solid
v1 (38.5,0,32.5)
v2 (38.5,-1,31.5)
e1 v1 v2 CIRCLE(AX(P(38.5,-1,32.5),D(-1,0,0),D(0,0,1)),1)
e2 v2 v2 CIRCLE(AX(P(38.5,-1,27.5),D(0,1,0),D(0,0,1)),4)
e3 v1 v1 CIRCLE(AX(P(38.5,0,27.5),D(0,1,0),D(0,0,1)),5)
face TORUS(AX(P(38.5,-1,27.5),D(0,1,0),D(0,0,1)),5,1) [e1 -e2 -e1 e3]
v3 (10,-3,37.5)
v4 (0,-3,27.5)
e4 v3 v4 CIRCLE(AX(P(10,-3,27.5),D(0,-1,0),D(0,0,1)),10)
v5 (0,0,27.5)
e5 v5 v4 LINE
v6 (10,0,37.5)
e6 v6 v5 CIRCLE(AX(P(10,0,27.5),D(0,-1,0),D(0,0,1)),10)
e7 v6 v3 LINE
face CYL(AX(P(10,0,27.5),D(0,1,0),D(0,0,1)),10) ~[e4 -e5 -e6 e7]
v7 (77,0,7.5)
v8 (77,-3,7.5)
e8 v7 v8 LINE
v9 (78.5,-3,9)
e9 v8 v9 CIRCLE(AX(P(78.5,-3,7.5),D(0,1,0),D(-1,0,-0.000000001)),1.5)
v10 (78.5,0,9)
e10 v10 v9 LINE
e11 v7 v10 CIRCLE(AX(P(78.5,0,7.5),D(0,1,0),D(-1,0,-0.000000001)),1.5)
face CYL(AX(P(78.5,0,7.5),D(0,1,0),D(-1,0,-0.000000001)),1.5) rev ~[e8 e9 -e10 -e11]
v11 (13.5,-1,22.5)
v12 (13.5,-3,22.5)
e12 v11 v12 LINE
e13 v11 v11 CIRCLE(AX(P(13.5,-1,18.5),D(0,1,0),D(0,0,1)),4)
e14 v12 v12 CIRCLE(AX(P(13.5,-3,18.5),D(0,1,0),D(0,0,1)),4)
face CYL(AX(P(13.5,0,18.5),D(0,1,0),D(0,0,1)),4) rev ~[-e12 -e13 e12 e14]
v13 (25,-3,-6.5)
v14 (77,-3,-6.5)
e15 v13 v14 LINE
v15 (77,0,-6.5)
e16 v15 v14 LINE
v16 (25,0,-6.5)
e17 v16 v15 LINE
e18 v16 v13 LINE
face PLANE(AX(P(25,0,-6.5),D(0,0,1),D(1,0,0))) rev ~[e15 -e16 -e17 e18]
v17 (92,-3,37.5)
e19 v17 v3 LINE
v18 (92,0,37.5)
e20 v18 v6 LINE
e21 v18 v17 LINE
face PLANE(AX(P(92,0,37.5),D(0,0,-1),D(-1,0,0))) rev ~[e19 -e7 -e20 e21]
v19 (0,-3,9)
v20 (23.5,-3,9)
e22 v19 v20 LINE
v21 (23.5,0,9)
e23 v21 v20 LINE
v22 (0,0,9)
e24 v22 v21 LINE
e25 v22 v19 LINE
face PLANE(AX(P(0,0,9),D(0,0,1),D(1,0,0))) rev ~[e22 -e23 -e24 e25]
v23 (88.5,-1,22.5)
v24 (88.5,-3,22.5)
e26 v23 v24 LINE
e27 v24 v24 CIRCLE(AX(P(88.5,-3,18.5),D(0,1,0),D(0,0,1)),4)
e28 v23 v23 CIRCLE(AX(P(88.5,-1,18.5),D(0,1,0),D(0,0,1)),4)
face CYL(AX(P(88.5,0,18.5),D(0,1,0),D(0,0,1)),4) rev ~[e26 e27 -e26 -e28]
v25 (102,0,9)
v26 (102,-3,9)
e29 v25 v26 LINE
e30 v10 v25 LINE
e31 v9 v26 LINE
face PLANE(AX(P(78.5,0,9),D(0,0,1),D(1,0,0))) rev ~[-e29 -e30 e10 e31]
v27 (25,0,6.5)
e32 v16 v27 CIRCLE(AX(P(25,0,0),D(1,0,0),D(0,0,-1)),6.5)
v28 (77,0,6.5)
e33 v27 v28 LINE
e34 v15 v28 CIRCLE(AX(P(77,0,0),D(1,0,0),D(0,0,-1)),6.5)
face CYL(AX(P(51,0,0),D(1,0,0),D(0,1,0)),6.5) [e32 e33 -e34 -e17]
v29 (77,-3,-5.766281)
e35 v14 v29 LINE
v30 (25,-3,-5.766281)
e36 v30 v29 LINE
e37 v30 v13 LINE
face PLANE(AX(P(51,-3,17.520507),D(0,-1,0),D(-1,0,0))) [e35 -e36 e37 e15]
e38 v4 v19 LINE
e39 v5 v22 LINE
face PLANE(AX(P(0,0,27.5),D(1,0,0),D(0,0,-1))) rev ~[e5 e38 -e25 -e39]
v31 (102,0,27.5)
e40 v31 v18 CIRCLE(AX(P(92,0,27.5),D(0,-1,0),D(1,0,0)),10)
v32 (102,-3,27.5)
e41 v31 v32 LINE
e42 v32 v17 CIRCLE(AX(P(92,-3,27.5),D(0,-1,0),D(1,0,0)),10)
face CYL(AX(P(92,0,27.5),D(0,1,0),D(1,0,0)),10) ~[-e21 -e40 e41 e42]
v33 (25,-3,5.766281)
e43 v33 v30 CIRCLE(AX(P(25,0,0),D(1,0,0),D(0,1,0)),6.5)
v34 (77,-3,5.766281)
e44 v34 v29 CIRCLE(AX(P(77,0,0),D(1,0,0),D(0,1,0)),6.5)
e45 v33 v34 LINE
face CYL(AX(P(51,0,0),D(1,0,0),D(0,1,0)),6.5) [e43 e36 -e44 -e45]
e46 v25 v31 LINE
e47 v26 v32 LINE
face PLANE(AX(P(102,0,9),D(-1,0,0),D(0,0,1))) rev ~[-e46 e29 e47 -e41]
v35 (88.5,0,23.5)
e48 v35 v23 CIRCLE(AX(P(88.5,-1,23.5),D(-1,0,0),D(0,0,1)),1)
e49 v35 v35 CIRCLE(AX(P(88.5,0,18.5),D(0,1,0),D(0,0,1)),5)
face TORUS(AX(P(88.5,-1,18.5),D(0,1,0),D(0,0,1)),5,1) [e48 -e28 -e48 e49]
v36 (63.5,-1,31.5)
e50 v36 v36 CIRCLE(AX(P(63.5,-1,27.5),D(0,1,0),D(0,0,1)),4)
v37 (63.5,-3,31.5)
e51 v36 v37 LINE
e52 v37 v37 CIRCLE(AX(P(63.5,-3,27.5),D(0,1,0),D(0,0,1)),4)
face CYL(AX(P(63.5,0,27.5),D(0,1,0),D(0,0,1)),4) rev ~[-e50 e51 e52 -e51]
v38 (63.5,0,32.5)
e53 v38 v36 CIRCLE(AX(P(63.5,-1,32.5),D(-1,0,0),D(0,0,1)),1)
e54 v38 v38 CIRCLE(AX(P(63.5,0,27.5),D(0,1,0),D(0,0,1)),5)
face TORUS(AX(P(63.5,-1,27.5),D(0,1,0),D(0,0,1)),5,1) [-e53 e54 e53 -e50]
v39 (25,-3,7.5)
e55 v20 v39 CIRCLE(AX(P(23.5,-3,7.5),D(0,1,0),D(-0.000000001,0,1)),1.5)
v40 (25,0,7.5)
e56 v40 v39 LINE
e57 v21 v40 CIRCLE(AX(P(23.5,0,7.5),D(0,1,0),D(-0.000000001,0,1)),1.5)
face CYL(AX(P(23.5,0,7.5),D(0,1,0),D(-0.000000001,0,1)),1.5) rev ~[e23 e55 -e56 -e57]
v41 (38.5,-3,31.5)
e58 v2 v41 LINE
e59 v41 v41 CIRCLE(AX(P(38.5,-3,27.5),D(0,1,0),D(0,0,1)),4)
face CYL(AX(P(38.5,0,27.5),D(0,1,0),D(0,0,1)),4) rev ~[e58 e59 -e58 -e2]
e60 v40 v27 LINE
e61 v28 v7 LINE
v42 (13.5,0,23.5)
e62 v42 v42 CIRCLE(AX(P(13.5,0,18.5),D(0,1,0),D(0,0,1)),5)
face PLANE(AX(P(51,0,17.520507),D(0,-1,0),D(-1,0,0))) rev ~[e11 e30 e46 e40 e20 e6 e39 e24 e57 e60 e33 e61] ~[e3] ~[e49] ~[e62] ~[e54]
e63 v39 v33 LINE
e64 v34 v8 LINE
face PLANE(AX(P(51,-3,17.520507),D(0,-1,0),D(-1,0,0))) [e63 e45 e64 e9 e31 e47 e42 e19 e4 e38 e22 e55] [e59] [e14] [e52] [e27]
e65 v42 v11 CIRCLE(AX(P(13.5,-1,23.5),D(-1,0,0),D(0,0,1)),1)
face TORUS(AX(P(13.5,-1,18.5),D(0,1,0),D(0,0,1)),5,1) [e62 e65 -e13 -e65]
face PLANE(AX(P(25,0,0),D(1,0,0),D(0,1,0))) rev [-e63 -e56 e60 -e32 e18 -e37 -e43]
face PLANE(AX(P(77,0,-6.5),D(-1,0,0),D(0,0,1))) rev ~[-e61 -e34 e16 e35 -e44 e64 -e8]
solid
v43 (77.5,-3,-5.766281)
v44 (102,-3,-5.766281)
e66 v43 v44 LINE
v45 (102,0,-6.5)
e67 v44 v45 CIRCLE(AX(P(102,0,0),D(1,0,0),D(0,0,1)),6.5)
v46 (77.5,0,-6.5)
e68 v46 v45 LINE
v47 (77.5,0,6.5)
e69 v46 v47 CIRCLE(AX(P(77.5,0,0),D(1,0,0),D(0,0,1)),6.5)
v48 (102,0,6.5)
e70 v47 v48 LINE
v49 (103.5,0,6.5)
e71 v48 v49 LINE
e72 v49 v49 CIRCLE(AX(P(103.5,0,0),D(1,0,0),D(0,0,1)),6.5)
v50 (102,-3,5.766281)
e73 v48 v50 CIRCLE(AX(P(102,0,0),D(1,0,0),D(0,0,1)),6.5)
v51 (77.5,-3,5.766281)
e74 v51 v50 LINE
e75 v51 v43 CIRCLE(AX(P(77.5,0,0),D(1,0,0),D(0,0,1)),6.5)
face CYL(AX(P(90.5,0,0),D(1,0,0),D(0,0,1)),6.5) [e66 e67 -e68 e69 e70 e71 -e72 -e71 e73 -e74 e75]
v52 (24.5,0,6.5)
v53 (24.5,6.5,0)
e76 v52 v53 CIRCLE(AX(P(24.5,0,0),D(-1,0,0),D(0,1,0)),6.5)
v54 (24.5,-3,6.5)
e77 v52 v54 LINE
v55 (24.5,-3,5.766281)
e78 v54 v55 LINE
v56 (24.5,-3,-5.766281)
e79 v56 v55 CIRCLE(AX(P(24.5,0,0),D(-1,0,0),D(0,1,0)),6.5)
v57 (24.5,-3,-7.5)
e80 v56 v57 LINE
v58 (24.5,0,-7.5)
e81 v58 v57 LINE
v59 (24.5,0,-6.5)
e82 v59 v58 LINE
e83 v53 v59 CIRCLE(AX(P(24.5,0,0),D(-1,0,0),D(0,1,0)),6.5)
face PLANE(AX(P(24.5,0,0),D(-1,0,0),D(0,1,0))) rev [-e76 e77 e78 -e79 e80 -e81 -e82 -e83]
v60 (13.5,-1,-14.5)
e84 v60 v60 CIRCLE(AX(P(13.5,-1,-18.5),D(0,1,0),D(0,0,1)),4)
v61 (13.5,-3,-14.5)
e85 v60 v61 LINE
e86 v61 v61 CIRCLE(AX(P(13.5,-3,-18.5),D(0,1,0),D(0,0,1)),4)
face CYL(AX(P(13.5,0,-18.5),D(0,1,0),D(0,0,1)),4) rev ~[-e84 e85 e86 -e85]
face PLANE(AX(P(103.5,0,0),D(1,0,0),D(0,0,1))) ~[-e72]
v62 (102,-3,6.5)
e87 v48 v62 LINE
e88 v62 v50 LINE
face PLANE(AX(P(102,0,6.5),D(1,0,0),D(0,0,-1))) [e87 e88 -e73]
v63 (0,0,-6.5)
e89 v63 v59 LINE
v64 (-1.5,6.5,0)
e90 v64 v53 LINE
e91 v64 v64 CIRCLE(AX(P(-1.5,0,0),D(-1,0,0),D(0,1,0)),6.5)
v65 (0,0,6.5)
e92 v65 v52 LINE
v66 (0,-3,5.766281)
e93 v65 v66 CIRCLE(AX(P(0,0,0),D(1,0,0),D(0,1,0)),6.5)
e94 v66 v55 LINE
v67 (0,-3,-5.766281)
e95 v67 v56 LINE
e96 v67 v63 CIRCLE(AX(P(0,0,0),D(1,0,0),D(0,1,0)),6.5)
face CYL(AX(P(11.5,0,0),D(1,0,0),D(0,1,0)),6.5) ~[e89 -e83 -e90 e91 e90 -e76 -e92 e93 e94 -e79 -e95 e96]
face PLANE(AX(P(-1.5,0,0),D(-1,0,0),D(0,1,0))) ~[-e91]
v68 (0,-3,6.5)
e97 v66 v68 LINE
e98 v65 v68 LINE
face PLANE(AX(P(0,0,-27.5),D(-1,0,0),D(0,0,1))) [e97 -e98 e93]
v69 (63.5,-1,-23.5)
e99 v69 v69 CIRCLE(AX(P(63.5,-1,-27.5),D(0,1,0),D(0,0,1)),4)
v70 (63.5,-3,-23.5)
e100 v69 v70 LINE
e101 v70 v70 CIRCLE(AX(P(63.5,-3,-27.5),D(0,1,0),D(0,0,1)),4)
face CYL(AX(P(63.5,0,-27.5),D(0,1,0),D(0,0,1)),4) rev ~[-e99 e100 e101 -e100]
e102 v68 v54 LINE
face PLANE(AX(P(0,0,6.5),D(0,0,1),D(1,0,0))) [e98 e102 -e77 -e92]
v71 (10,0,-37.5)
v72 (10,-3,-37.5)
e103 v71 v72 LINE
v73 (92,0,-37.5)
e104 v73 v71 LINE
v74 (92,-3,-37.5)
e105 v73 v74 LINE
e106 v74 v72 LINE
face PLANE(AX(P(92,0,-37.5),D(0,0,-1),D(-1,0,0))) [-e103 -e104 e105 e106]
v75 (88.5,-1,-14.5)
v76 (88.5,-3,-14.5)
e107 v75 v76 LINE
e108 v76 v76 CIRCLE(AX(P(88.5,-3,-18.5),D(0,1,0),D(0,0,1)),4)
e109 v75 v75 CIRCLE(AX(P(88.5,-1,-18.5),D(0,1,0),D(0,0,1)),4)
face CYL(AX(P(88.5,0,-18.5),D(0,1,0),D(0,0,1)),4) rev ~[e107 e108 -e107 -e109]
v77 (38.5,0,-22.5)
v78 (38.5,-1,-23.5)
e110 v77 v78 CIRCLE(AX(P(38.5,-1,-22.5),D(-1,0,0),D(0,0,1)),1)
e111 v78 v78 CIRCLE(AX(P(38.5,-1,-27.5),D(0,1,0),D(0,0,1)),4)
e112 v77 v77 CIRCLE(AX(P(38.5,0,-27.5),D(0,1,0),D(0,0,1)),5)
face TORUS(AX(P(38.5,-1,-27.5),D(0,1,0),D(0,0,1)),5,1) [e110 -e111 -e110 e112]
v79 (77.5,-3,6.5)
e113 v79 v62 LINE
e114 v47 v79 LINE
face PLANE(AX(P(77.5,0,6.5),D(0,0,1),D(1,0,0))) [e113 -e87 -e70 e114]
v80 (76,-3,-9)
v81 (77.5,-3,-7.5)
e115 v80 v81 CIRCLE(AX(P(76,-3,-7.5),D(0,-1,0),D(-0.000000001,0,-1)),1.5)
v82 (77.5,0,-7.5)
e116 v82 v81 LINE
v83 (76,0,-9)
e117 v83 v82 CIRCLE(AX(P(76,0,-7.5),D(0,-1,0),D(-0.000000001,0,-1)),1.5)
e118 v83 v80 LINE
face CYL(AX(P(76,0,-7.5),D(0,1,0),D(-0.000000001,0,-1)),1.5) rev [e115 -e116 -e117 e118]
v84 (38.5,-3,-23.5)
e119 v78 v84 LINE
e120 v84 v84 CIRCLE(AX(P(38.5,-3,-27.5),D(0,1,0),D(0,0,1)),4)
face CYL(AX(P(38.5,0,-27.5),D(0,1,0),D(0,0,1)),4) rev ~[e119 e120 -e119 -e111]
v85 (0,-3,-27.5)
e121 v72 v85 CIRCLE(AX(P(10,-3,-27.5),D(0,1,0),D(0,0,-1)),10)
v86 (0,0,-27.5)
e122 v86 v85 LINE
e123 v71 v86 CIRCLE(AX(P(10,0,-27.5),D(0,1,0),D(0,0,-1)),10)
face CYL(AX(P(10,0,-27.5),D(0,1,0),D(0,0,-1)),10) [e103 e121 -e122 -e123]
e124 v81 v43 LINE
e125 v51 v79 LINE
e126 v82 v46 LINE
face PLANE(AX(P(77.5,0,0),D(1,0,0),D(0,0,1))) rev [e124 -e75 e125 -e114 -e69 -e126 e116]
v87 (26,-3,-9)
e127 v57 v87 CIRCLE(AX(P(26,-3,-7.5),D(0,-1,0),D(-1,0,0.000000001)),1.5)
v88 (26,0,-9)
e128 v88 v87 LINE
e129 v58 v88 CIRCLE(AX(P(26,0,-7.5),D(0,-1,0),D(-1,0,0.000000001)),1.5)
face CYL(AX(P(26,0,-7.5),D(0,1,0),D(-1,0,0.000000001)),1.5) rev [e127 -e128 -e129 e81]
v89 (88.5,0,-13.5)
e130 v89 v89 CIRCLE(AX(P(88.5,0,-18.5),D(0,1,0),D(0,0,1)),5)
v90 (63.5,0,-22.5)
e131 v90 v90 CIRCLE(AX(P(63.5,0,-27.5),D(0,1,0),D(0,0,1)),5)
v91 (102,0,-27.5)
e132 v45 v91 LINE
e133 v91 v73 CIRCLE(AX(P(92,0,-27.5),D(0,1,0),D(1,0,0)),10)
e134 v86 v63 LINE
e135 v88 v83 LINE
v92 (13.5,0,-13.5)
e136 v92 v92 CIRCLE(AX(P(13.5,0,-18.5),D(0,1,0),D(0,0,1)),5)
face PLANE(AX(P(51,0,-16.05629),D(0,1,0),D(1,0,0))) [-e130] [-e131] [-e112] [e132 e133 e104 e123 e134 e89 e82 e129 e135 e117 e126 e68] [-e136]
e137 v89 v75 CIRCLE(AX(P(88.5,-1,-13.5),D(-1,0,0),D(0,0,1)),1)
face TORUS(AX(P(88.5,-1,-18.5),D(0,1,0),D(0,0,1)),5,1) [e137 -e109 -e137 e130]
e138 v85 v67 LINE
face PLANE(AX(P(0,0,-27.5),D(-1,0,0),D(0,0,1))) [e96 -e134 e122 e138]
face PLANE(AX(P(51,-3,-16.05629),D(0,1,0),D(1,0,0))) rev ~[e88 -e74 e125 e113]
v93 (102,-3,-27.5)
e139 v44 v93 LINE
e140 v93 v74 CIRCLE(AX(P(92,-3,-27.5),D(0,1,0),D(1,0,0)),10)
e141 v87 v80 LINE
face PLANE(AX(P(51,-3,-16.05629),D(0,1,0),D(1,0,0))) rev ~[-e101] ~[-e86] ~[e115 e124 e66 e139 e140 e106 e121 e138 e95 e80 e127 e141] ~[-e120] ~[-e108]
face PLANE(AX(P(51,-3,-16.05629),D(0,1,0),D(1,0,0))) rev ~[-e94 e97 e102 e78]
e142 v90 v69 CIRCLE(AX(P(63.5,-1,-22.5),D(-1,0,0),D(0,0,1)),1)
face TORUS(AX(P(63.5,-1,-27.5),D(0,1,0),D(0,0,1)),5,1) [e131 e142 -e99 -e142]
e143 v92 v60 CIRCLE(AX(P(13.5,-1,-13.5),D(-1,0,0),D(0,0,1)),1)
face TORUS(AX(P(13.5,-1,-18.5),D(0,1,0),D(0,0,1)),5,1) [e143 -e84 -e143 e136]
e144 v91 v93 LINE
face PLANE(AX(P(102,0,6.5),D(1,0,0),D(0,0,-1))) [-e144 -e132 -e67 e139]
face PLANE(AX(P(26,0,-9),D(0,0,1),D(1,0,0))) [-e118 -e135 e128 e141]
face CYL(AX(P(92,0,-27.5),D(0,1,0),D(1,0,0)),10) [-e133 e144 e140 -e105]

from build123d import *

# Parameters (mm, degrees)
HINGE_LEAVES_3MM_DEPTH        = 3
HINGE_LEAVES_3MM_2_DEPTH      = 3
SCREW_HOLES_PROFILE_R         = 4
SCREW_HOLES_8X_8_DEPTH        = 3
SCREW_HOLE_EDGE_FILLET_R1_A_R = 1
SCREW_HOLE_EDGE_FILLET_R1_B_R = 1
END_KNUCKLE_1_PROFILE_W       = 26
END_KNUCKLE_1_PROFILE_H       = 6.5
CENTRE_KNUCKLE_PROFILE_W      = 52
CENTRE_KNUCKLE_PROFILE_H      = 6.5
END_KNUCKLE_2_PROFILE_W       = 26
END_KNUCKLE_2_PROFILE_H       = 6.5


with BuildPart() as part:
    # Hinge Leaves Profile → Hinge Leaves 3mm (new body)
    with BuildSketch(Plane(origin=(0, 0, 0), x_dir=(1, 0, 0), z_dir=(0, 1, 0))):
        with BuildLine():
            Line((0, 0), (0, -6.5))
            Line((0, -6.5), (24.5, -6.5))
            Line((24.5, -6.5), (24.5, 7.5))
            ThreePointArc((24.5, 7.5), (24.939339828, 8.560660172), (26, 9))
            Line((26, 9), (76, 9))
            ThreePointArc((76, 9), (77.060660172, 8.560660172), (77.5, 7.5))
            Line((77.5, 7.5), (77.5, -6.5))
            Line((77.5, -6.5), (102, -6.5))
            Line((102, -6.5), (102, 27.5))
            ThreePointArc((102, 27.5), (99.071067812, 34.571067812), (92, 37.5))
            Line((92, 37.5), (10, 37.5))
            ThreePointArc((10, 37.5), (2.928932188, 34.571067812), (0, 27.5))
            Line((0, 27.5), (0, 0))
        make_face()
    extrude(amount=-HINGE_LEAVES_3MM_DEPTH)


with BuildPart() as body_2:
    # Hinge Leaves Profile → Hinge Leaves 3mm 2 (new body)
    with BuildSketch(Plane(origin=(0, 0, 0), x_dir=(1, 0, 0), z_dir=(0, 1, 0))):
        with BuildLine():
            Line((0, -9), (23.5, -9))
            ThreePointArc((23.5, -9), (24.560660172, -8.560660172), (25, -7.5))
            Line((25, -7.5), (25, 6.5))
            Line((25, 6.5), (77, 6.5))
            Line((77, 6.5), (77, -7.5))
            ThreePointArc((77, -7.5), (77.439339828, -8.560660172), (78.5, -9))
            Line((78.5, -9), (102, -9))
            Line((102, -9), (102, -27.5))
            ThreePointArc((102, -27.5), (99.071067812, -34.571067812), (92, -37.5))
            Line((92, -37.5), (10, -37.5))
            ThreePointArc((10, -37.5), (2.928932188, -34.571067812), (0, -27.5))
            Line((0, -27.5), (0, -9))
        make_face()
    extrude(amount=-HINGE_LEAVES_3MM_2_DEPTH)


with BuildPart() as screw_holes_8x_8_tool:
    # Screw Holes Profile → Screw Holes 8xØ8 (new body)
    with BuildSketch(Plane(origin=(0, 0, 0), x_dir=(1, 0, 0), z_dir=(0, 1, 0))):
        with Locations(Location((13.5, 18.5, 0), (0, 0, 270))):
            Circle(SCREW_HOLES_PROFILE_R)
        with Locations(Location((38.5, 27.5, 0), (0, 0, 270))):
            Circle(SCREW_HOLES_PROFILE_R)
        with Locations(Location((63.5, 27.5, 0), (0, 0, 270))):
            Circle(SCREW_HOLES_PROFILE_R)
        with Locations(Location((88.5, 18.5, 0), (0, 0, 270))):
            Circle(SCREW_HOLES_PROFILE_R)
        with Locations(Location((13.5, -18.5, 0), (0, 0, 270))):
            Circle(SCREW_HOLES_PROFILE_R)
        with Locations(Location((38.5, -27.5, 0), (0, 0, 270))):
            Circle(SCREW_HOLES_PROFILE_R)
        with Locations(Location((63.5, -27.5, 0), (0, 0, 270))):
            Circle(SCREW_HOLES_PROFILE_R)
        with Locations(Location((88.5, -18.5, 0), (0, 0, 270))):
            Circle(SCREW_HOLES_PROFILE_R)
    extrude(amount=-SCREW_HOLES_8X_8_DEPTH)


with BuildPart() as part_1:
    add(part.part)

    # Screw Holes 8xØ8: cut by screw_holes_8x_8_tool
    add(screw_holes_8x_8_tool.part, mode=Mode.SUBTRACT)

    # Screw Hole Edge Fillet R1 A
    screw_hole_edge_fillet_r1_a_edges = [part_1.edges().sort_by_distance(p)[0] for p in [
        (13.5, 0, -22.5),
        (38.5, 0, -31.5),
        (63.5, 0, -31.5),
        (88.5, 0, -22.5),
    ]]
    fillet(screw_hole_edge_fillet_r1_a_edges, radius=SCREW_HOLE_EDGE_FILLET_R1_A_R)

    # End Knuckle 1 Profile → End Knuckle 1 Ø13x26 (revolve)
    with BuildSketch(Plane.XY):
        with Locations((11.5, 3.25)):
            Rectangle(END_KNUCKLE_1_PROFILE_W, END_KNUCKLE_1_PROFILE_H)
    revolve(axis=Axis((24.5, 0, 0), (-1, 0, 0)))

    # End Knuckle 2 Profile → End Knuckle 2 Ø13x26 (revolve)
    with BuildSketch(Plane.XY, mode=Mode.PRIVATE) as end_knuckle_2_13x26_sk:
        with Locations((90.5, 3.25)):
            Rectangle(END_KNUCKLE_2_PROFILE_W, END_KNUCKLE_2_PROFILE_H)
    revolve(end_knuckle_2_13x26_sk.sketch.rotate(Axis((77.5, 0, 0), (1, 0, 0)), 90), axis=Axis((77.5, 0, 0), (1, 0, 0)))


with BuildPart() as body_2_1:
    add(body_2.part)

    # Screw Holes 8xØ8: cut by screw_holes_8x_8_tool
    add(screw_holes_8x_8_tool.part, mode=Mode.SUBTRACT)

    # Screw Hole Edge Fillet R1 B
    screw_hole_edge_fillet_r1_b_edges = [body_2_1.edges().sort_by_distance(p)[0] for p in [
        (13.5, 0, 14.5),
        (38.5, 0, 23.5),
        (63.5, 0, 23.5),
        (88.5, 0, 14.5),
    ]]
    fillet(screw_hole_edge_fillet_r1_b_edges, radius=SCREW_HOLE_EDGE_FILLET_R1_B_R)

    # Centre Knuckle Profile → Centre Knuckle Ø13x52 (revolve)
    with BuildSketch(Plane.XY):
        with Locations((51, 3.25)):
            Rectangle(CENTRE_KNUCKLE_PROFILE_W, CENTRE_KNUCKLE_PROFILE_H)
    revolve(axis=Axis((25, 0, 0), (1, 0, 0)))


solid = Compound([part_1.part, body_2_1.part])
